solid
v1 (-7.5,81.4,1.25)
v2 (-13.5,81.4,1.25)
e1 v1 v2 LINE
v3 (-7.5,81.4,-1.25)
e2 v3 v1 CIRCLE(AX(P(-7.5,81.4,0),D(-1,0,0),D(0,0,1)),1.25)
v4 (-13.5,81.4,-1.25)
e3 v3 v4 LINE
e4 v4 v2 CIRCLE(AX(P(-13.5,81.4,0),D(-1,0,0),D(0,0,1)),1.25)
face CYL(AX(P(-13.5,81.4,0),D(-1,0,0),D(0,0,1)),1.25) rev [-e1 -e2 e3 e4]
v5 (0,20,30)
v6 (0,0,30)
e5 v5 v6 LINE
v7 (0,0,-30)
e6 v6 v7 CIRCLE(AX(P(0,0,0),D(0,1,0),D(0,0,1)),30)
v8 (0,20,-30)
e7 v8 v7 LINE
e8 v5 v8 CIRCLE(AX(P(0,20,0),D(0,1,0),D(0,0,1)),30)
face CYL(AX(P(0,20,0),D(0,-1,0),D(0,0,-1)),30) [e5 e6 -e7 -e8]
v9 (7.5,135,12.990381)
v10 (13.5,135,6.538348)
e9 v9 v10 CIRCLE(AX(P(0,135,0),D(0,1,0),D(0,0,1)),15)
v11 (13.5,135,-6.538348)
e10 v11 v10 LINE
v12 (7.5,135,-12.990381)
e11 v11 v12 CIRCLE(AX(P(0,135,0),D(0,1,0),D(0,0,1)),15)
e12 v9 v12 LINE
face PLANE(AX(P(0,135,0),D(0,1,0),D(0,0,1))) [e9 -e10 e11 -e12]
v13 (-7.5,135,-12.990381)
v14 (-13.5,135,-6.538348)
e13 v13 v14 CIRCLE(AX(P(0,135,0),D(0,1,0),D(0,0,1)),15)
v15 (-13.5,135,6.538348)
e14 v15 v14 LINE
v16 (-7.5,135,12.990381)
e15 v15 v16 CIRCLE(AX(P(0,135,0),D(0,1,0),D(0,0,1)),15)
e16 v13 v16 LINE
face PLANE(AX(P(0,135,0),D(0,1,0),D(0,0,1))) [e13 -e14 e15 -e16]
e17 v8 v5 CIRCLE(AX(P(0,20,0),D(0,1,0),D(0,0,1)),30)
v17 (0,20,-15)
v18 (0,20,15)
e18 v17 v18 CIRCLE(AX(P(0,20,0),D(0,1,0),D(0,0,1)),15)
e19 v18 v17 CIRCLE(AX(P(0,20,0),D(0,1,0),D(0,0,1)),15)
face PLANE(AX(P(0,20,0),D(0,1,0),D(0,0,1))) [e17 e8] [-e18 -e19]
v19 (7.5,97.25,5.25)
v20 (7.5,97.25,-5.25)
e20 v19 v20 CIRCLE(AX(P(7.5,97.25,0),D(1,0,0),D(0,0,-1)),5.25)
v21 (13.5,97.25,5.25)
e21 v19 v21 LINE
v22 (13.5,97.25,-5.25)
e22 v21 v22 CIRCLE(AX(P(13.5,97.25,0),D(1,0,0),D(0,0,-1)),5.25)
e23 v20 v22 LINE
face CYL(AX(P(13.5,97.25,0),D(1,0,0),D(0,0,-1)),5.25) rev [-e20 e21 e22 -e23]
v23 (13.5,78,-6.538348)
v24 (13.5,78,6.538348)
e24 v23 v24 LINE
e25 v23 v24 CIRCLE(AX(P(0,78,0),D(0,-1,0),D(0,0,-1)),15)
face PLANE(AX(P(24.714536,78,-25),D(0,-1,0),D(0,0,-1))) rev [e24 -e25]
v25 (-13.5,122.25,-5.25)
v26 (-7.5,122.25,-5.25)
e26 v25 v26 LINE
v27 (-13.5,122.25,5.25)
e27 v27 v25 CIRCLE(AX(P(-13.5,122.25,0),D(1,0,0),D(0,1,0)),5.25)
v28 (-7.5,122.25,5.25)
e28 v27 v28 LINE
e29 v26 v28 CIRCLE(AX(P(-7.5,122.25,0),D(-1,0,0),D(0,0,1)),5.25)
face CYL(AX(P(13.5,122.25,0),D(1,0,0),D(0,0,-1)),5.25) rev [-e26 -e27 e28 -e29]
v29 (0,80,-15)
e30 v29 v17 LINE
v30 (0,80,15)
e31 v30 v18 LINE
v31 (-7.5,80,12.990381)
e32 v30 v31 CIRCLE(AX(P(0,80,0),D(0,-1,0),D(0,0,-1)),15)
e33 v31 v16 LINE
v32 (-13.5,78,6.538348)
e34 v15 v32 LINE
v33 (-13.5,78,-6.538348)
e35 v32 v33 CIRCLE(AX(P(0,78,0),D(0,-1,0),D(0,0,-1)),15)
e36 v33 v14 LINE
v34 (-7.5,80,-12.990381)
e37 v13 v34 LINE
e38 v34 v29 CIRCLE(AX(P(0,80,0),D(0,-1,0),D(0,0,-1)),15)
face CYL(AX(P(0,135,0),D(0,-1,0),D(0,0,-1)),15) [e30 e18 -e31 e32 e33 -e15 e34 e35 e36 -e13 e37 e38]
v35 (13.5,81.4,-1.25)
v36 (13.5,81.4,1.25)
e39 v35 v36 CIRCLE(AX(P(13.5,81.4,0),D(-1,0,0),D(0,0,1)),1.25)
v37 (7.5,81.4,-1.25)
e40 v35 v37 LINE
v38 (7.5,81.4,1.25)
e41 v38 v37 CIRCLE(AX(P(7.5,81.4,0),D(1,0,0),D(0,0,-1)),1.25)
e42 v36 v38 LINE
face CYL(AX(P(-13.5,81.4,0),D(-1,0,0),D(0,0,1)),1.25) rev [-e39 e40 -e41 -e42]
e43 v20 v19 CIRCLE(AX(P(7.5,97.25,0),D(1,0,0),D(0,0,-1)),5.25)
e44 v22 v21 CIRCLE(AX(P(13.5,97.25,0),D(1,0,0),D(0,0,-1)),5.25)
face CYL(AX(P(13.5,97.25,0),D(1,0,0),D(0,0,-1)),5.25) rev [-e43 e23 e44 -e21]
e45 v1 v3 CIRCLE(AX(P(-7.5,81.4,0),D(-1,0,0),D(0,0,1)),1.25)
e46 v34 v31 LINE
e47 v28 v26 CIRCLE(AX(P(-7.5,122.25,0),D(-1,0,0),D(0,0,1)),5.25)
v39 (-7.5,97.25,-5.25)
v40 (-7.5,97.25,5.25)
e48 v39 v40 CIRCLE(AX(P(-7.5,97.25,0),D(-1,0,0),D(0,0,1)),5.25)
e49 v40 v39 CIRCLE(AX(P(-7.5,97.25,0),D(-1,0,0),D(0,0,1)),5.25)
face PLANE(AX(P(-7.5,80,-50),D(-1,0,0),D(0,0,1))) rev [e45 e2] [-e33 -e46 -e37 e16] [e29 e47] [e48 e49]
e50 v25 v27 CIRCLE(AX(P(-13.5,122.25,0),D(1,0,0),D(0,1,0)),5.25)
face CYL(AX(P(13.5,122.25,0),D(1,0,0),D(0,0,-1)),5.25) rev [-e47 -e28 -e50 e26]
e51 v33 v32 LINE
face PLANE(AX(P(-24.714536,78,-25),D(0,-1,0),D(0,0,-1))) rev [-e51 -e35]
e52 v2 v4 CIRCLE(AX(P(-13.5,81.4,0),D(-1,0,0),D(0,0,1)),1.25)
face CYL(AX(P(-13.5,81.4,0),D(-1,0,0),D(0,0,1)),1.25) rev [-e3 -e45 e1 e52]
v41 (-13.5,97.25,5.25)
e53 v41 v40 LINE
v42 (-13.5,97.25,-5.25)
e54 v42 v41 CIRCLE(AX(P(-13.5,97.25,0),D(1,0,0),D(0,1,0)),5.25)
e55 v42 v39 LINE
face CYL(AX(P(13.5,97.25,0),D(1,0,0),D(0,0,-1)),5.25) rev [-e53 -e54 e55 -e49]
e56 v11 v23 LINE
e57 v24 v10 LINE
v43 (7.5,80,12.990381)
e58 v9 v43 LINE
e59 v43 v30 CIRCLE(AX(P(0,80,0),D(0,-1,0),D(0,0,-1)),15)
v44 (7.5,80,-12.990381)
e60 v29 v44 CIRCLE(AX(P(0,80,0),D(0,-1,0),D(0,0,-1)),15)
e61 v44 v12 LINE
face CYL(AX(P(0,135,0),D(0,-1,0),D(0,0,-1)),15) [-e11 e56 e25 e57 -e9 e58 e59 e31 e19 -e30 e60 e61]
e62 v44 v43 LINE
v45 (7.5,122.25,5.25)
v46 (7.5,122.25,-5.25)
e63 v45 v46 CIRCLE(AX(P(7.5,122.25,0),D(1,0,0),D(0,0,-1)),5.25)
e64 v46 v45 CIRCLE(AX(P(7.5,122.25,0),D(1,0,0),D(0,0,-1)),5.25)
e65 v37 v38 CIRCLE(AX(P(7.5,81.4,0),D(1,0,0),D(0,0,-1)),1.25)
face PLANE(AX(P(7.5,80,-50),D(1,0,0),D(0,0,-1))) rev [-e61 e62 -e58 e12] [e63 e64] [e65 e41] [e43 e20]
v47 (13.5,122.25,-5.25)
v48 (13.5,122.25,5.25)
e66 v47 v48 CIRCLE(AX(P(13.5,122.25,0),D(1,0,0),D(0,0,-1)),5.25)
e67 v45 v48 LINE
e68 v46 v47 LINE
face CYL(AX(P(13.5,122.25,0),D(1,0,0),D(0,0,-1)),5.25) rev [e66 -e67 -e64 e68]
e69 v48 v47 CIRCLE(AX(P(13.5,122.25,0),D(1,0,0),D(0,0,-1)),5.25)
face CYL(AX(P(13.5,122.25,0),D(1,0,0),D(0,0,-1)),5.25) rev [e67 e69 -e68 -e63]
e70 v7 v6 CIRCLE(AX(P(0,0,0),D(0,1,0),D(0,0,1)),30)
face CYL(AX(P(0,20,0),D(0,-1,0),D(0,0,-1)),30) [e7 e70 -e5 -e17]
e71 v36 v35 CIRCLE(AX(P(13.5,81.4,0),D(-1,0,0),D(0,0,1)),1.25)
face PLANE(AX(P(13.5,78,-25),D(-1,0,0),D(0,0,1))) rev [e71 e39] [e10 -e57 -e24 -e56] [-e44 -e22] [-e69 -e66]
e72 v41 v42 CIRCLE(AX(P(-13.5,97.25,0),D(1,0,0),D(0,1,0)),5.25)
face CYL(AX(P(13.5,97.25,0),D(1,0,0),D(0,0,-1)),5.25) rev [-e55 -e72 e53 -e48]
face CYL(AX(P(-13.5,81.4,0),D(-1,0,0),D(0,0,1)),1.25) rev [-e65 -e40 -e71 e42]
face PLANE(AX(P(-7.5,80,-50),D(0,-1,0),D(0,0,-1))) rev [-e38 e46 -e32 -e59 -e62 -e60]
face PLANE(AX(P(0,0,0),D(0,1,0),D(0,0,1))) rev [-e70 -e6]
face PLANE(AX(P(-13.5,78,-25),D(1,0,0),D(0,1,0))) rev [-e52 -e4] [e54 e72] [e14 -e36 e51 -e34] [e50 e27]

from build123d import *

# Parameters (mm, degrees)
SKETCH_1_R                = 30
EXTRUDE_1_DEPTH           = 20
SKETCH_2_R                = 15
EXTRUDE_2_DEPTH           = 115
SKETCH_3_W                = 15
SKETCH_3_H                = 65.275195259
CUT_EXTRUDE_1_DEPTH       = 50
SKETCH_4_W                = 11.214536165
SKETCH_4_H                = 73.146220951
CUT_EXTRUDE_2_DEPTH       = 25
HOLE_WIZARD_10_5_10_5_1_D = 10.5
HOLE_WIZARD_M3_1_D        = 2.5


with BuildPart() as part:
    # 草图1 → 凸台-拉伸1 (new body)
    with BuildSketch(Plane(origin=(0, 0, 0), x_dir=(1, 0, 0), z_dir=(0, 1, 0))):
        with Locations(Location((0, 0, 0), (0, 0, 270))):
            Circle(SKETCH_1_R)
    extrude(amount=EXTRUDE_1_DEPTH)

    # 草图2 → 凸台-拉伸2 (add)
    with BuildSketch(Plane(origin=(0, 20, 0), x_dir=(1, 0, 0), z_dir=(0, 1, 0))):
        with Locations(Location((0, 0, 0), (0, 0, 270))):
            Circle(SKETCH_2_R)
    extrude(amount=EXTRUDE_2_DEPTH)

    # 草图3 → 切除-拉伸1 (cut, symmetric)
    with BuildSketch(Plane.XY):
        with Locations((0, 112.63759763)):
            Rectangle(SKETCH_3_W, SKETCH_3_H)
    extrude(amount=CUT_EXTRUDE_1_DEPTH, both=True, mode=Mode.SUBTRACT)

    # 草图4 → 切除-拉伸2 (cut, symmetric)
    with BuildSketch(Plane.XY):
        with Locations((19.107268082, 114.573110476)):
            Rectangle(SKETCH_4_W, SKETCH_4_H)
        with Locations((-19.107268082, 114.573110476)):
            Rectangle(SKETCH_4_W, SKETCH_4_H)
    extrude(amount=CUT_EXTRUDE_2_DEPTH, both=True, mode=Mode.SUBTRACT)

    # Ø10.5 (10.5) 直径孔1 (through all)
    with Locations(Plane(origin=(13.5, 0, 0), x_dir=(0, 0, -1), z_dir=(1, 0, 0))):
        with Locations((0, 97.25), (0, 122.25)):
            Hole(HOLE_WIZARD_10_5_10_5_1_D / 2)

    # M3 螺纹孔1 (through all)
    with Locations(Plane.ZY.offset(13.5)):
        with Locations((0, 81.4)):
            Hole(HOLE_WIZARD_M3_1_D / 2)


solid = part.part
